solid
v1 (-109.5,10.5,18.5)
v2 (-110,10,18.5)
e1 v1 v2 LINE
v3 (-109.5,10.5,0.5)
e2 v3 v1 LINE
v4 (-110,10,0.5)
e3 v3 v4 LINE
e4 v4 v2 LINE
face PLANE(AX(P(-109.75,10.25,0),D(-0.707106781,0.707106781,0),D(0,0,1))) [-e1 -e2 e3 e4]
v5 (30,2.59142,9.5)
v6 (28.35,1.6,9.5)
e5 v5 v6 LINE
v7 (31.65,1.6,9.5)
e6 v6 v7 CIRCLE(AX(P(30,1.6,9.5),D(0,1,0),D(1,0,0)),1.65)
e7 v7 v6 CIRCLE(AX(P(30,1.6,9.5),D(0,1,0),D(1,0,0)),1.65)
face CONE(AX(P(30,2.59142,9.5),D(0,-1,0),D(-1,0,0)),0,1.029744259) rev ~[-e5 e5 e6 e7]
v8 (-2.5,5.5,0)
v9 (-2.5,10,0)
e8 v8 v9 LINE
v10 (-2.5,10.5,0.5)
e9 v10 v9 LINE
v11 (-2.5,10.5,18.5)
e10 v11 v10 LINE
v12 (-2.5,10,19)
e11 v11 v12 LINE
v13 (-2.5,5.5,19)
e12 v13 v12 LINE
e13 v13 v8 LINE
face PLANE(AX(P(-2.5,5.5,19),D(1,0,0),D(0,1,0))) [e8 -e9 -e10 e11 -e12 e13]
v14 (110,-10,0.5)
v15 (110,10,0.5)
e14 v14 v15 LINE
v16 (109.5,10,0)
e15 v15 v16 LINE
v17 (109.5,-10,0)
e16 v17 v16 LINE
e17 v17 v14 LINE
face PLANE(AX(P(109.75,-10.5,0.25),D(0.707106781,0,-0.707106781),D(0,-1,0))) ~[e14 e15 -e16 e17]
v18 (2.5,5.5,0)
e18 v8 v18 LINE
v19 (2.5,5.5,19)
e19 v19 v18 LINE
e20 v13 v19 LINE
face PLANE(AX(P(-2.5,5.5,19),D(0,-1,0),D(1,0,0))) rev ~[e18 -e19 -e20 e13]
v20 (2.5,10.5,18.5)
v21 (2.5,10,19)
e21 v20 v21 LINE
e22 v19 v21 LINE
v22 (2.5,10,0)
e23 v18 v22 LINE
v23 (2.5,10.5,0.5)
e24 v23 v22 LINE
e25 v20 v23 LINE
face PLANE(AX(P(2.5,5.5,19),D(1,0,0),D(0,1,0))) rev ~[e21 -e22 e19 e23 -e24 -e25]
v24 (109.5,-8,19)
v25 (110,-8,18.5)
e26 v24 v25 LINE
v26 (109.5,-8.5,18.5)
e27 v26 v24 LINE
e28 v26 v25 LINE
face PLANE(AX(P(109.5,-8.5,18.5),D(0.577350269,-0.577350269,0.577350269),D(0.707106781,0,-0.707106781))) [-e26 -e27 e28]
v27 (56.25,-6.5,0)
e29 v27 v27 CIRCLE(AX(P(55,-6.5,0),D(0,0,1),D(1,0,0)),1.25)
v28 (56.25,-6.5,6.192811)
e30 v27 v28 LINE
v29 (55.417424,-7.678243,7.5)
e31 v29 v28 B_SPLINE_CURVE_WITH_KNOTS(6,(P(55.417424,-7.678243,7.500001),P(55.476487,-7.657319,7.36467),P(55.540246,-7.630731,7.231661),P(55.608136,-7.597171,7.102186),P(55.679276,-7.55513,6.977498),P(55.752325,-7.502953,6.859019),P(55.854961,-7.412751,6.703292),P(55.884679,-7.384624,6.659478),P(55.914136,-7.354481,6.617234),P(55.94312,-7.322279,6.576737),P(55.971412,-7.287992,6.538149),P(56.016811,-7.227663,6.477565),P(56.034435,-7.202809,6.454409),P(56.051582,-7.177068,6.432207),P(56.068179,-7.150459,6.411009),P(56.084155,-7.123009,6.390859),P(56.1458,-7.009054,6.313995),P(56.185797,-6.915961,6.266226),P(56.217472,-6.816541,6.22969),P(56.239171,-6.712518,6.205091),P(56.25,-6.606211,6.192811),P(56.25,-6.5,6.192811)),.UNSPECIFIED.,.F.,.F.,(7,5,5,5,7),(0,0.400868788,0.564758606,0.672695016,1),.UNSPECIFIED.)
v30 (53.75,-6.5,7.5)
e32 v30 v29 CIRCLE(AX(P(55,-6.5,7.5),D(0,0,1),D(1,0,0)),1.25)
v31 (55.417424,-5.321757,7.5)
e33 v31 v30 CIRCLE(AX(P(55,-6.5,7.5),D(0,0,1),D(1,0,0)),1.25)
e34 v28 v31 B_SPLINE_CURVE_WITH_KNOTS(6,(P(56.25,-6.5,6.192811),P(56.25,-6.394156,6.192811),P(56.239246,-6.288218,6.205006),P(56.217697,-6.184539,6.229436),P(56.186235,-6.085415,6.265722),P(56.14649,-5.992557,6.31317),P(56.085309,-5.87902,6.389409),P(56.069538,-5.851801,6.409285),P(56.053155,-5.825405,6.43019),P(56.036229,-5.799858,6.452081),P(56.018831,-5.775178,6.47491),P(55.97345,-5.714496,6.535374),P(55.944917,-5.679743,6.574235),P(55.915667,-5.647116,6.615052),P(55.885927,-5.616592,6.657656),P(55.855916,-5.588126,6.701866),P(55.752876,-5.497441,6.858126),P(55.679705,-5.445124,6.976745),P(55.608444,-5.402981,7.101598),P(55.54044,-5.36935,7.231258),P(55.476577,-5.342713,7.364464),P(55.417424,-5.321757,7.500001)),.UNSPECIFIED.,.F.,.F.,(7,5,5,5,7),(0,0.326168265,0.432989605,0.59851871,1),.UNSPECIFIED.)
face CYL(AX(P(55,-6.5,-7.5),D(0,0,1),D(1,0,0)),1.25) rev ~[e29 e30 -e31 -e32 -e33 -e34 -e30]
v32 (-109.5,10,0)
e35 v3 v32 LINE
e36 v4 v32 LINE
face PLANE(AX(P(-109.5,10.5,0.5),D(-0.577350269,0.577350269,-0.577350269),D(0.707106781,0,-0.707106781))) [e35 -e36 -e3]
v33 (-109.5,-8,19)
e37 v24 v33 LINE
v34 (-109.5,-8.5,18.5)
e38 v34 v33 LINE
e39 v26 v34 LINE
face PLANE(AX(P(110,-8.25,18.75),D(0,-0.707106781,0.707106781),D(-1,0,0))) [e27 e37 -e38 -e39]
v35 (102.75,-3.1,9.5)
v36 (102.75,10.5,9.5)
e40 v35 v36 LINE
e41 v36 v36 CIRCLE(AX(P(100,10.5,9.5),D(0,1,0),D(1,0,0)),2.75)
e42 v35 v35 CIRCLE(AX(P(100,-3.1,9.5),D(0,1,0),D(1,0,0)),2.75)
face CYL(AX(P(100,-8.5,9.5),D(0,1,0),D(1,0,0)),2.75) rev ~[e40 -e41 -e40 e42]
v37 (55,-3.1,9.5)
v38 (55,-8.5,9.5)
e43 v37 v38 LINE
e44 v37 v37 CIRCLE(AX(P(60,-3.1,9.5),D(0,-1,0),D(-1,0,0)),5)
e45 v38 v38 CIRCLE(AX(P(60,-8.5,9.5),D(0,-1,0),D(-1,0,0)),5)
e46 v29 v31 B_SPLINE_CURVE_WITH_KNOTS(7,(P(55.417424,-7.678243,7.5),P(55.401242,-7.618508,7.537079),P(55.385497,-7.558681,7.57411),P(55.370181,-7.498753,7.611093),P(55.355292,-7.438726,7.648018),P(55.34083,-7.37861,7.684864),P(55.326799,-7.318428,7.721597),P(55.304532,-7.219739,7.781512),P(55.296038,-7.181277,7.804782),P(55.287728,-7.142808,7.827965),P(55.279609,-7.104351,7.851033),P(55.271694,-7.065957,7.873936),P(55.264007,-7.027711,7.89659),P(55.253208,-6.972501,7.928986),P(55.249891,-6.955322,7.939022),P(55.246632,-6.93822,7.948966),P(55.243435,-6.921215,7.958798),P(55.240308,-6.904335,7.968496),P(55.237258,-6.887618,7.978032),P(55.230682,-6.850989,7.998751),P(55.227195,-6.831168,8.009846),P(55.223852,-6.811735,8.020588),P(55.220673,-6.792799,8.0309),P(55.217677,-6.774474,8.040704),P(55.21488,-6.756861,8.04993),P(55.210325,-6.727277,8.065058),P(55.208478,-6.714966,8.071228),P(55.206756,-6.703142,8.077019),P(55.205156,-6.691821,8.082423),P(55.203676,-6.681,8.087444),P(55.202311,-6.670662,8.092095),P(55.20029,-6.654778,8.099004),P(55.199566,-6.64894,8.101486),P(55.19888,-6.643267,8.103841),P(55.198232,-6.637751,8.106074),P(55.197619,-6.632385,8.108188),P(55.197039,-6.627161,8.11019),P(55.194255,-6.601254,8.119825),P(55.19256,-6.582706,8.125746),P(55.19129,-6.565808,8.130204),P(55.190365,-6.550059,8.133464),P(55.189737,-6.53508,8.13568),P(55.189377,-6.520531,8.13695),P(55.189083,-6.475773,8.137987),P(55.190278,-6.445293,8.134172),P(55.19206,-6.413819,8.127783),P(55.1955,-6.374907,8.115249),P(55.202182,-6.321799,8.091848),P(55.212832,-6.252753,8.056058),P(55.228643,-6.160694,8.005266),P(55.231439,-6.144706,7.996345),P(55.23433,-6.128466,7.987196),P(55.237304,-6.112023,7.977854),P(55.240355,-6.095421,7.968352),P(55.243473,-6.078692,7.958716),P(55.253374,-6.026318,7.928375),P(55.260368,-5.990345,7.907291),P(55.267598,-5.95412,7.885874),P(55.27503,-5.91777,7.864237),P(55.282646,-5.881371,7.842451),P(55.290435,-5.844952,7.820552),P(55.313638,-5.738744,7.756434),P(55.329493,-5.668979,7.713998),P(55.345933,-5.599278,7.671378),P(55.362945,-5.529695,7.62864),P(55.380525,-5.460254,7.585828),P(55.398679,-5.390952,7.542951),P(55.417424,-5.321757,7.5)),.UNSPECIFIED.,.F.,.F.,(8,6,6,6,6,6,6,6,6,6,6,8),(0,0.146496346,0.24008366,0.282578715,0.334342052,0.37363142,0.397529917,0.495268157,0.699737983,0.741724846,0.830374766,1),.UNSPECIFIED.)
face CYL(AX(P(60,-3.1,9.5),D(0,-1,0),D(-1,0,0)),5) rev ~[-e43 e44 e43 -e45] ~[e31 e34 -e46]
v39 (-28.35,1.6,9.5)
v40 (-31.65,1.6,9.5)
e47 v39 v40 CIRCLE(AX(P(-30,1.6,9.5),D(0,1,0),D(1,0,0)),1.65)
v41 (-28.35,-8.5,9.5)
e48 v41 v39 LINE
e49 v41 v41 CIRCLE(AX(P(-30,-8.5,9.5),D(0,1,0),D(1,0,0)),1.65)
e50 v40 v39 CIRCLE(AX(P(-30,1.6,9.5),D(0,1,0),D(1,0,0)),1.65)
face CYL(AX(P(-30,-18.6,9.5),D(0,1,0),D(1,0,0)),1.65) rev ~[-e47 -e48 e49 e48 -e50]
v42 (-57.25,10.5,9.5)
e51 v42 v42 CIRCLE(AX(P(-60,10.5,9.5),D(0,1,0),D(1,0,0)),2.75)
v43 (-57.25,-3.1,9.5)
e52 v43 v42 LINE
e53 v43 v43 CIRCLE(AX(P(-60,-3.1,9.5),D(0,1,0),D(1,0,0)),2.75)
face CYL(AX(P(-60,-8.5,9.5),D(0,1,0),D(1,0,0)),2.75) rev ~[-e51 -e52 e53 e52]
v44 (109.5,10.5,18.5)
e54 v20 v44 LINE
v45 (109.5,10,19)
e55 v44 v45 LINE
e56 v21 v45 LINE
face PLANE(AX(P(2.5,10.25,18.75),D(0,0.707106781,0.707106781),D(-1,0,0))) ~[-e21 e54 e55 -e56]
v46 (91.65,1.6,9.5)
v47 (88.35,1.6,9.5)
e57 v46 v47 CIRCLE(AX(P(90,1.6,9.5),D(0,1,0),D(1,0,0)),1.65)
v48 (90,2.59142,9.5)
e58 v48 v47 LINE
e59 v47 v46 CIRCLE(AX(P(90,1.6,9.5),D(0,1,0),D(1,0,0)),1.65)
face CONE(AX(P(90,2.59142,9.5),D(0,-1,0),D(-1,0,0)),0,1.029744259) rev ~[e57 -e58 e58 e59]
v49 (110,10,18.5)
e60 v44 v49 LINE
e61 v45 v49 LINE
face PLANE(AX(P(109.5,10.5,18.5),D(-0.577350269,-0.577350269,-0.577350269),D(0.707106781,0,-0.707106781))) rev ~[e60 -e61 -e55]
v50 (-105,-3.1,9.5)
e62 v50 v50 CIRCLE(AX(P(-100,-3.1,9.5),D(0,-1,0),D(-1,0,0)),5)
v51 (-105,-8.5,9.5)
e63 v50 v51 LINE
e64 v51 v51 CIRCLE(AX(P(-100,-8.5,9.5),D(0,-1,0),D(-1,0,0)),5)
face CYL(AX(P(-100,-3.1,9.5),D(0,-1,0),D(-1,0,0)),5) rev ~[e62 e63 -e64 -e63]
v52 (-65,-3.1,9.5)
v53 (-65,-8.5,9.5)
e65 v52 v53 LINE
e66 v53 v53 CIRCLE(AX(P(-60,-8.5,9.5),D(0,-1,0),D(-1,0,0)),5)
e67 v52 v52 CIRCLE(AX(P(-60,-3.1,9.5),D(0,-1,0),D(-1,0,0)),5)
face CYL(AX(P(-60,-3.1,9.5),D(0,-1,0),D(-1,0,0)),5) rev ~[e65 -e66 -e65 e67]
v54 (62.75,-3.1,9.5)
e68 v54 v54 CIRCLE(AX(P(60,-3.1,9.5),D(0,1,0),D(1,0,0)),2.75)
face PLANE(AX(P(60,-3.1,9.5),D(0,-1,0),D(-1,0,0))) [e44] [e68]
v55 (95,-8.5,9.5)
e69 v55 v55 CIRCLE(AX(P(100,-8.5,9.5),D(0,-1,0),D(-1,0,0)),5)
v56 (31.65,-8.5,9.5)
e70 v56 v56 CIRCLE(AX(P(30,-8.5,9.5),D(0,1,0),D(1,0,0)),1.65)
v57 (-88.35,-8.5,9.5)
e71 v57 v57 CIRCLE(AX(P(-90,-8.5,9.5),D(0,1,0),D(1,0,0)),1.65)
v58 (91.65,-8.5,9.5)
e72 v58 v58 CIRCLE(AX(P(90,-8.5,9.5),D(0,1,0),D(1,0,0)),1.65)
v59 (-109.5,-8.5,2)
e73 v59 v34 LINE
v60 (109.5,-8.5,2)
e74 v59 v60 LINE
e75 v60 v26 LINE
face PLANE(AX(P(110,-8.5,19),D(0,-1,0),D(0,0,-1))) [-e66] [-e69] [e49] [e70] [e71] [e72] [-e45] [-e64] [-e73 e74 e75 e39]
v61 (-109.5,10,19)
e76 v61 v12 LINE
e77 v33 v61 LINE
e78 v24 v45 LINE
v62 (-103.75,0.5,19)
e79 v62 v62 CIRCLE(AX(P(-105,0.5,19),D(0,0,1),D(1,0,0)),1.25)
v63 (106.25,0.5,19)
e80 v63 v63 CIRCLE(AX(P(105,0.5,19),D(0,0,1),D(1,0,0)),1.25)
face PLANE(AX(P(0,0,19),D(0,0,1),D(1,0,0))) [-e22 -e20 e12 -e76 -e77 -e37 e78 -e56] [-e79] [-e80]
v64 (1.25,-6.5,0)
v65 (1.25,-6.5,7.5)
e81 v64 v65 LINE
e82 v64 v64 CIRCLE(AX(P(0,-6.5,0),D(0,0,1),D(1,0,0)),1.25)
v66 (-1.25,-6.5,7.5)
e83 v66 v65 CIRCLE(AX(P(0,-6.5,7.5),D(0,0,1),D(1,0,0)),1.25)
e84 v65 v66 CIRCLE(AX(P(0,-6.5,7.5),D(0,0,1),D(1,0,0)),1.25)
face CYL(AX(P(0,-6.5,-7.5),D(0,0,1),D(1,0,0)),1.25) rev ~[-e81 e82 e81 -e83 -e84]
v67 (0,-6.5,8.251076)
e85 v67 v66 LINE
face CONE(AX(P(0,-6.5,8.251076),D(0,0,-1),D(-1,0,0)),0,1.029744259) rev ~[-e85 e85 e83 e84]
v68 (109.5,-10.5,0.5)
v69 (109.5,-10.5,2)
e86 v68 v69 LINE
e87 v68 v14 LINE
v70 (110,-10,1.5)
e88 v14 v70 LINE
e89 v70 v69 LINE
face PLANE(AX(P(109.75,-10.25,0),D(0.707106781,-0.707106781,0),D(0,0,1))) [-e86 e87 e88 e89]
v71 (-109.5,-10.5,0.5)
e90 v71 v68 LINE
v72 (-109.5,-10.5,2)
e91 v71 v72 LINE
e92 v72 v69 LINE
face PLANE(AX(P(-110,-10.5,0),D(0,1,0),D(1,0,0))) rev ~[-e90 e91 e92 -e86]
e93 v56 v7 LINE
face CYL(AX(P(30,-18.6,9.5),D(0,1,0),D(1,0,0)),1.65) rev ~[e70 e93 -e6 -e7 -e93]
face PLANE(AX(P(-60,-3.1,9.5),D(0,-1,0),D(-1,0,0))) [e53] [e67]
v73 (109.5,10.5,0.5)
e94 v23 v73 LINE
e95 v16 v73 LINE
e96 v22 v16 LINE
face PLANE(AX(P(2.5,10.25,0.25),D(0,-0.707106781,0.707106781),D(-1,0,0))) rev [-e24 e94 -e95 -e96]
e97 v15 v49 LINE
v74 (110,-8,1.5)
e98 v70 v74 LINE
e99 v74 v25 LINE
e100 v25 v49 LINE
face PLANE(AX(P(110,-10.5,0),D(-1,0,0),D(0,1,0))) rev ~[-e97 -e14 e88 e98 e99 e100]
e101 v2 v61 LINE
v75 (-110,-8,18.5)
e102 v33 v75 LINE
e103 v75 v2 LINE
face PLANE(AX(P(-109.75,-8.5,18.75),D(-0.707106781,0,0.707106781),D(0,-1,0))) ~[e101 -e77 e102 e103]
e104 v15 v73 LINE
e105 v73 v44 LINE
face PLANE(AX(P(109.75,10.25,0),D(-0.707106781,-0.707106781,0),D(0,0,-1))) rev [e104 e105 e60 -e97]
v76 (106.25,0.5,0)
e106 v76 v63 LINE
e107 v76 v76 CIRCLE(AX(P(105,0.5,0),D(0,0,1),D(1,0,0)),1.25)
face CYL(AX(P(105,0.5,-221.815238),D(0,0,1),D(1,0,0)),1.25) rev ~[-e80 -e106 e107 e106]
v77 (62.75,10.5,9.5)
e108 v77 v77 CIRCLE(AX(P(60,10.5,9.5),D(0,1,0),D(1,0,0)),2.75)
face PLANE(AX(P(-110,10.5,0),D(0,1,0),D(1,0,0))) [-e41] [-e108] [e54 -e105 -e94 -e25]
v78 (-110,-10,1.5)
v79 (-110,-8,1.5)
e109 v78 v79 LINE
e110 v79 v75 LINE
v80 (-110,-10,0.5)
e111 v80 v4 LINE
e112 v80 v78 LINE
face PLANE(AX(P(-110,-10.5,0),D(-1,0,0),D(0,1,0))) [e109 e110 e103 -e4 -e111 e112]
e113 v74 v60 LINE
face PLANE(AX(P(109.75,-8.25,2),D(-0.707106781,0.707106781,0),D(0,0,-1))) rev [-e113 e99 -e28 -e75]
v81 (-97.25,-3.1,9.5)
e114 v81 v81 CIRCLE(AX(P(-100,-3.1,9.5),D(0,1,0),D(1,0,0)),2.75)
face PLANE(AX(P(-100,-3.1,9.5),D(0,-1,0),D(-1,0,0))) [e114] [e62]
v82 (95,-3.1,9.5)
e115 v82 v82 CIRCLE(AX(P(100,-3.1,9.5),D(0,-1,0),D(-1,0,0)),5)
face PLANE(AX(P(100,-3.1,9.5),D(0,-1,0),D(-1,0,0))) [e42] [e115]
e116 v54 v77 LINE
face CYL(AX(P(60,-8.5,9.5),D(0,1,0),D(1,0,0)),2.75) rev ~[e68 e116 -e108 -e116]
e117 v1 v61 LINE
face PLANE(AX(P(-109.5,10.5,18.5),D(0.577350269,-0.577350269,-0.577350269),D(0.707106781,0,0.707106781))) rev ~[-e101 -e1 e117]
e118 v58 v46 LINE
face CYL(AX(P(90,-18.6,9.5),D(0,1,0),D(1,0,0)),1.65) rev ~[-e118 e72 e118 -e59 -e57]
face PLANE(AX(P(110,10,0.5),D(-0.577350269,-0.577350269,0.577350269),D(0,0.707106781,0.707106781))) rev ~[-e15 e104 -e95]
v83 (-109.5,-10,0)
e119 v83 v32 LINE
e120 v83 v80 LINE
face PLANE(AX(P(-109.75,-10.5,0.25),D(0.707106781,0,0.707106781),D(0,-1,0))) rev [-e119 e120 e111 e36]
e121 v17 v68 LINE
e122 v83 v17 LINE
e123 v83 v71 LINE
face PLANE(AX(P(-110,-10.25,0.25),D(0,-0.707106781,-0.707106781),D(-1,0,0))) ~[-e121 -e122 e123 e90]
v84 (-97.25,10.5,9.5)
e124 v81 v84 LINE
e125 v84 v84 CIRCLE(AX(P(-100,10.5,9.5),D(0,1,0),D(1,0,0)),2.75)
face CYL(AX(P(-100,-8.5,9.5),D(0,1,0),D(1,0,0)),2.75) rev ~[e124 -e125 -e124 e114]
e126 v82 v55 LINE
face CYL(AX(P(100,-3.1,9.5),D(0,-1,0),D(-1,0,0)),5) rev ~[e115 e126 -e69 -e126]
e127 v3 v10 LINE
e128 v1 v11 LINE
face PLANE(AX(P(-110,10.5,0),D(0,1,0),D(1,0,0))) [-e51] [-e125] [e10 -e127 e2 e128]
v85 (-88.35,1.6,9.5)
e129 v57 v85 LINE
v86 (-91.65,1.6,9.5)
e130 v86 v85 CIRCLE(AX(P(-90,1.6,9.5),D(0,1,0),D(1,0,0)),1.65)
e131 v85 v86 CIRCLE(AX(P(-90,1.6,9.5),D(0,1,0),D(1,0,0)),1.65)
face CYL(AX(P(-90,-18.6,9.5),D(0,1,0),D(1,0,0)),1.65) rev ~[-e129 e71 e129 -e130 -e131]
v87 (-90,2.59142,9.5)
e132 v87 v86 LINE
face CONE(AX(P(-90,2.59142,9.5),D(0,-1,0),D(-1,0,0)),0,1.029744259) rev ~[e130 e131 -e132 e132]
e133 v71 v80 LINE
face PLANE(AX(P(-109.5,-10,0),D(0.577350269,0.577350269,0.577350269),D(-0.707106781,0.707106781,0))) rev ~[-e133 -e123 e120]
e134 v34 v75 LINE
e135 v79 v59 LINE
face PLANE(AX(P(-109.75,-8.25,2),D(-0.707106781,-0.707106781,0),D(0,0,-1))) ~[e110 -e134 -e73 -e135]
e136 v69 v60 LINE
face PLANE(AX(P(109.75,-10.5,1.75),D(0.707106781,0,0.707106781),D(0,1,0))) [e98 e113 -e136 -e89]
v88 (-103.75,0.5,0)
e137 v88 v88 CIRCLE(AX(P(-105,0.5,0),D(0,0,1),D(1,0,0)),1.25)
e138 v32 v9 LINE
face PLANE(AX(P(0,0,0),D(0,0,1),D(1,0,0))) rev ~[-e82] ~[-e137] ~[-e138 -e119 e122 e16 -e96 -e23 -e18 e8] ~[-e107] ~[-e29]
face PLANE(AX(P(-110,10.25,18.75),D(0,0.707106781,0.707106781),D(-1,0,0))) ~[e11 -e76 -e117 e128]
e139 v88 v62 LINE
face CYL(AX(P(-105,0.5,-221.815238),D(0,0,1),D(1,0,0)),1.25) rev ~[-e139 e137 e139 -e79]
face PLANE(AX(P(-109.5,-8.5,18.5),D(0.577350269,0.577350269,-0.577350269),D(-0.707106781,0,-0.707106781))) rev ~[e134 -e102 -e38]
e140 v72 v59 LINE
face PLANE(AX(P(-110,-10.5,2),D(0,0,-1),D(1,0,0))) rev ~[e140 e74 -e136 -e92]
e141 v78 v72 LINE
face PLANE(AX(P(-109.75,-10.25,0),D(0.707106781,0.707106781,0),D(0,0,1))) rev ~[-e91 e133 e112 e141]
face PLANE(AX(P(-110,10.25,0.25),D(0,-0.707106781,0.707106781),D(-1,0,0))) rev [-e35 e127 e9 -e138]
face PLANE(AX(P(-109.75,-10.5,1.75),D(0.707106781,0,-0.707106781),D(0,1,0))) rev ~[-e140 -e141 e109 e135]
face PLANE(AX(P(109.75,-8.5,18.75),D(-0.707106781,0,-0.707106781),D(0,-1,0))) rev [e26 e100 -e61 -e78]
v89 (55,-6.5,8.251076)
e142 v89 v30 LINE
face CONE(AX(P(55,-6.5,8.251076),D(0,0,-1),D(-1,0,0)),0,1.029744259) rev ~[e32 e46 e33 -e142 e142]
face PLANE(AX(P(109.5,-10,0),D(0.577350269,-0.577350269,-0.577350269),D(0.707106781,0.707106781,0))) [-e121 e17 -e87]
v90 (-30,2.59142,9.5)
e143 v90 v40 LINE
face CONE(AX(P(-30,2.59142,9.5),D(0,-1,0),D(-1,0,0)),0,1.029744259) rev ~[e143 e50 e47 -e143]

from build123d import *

# Parameters (mm, degrees)
SKETCH_1_W                   = 220
SKETCH_1_H                   = 21
EXTRUDE_1_DEPTH              = 19
SKETCH_2_W                   = 220
SKETCH_2_H                   = 15
CUT_EXTRUDE_1_DEPTH          = 2
HOLE_WIZARD_M4_1_D           = 3.3
HOLE_WIZARD_M4_1_DEPTH       = 10.1
HOLE_WIZARD_M4_1_TIP         = 0.991420021
HOLE_WIZARD_M5_1_D           = 5.5
HOLE_WIZARD_M5_1_CBORE_D     = 10
HOLE_WIZARD_M5_1_CBORE_DEPTH = 5.4
SKETCH_7_W                   = 5
SKETCH_7_H                   = 5
CUT_EXTRUDE_2_DEPTH          = 113.12158579
HOLE_WIZARD_M3_1_D           = 2.5
HOLE_WIZARD_M3_1_DEPTH       = 7.5
HOLE_WIZARD_M3_1_TIP         = 0.751075774
SKETCH_12_W                  = 2
SKETCH_12_H                  = 2
CUT_EXTRUDE_3_DEPTH          = 222.06842832
CHAMFER_1_SIZE               = 0.5
HOLE_WIZARD_M3_2_D           = 2.5


with BuildPart() as part:
    # 草图1 → 凸台-拉伸1 (new body)
    with BuildSketch(Plane.XY):
        Rectangle(SKETCH_1_W, SKETCH_1_H)
    extrude(amount=EXTRUDE_1_DEPTH)

    # 草图2 → 切除-拉伸1 (cut)
    with BuildSketch(Plane.XZ.offset(10.5)):
        with Locations((0, 9.5)):
            Rectangle(SKETCH_2_W, SKETCH_2_H)
    extrude(amount=-CUT_EXTRUDE_1_DEPTH, mode=Mode.SUBTRACT)

    # M4 螺纹孔1
    with Locations(Plane(origin=(0, -8.5, 0), x_dir=(-1, 0, 0), z_dir=(0, -1, 0))):
        with Locations((-90, -9.5), (-30, -9.5), (30, -9.5), (90, -9.5)):
            Hole(HOLE_WIZARD_M4_1_D / 2, depth=HOLE_WIZARD_M4_1_DEPTH)
            with Locations((0, 0, -(HOLE_WIZARD_M4_1_DEPTH + HOLE_WIZARD_M4_1_TIP / 2))):  # 118° drill point
                Cone(0, HOLE_WIZARD_M4_1_D / 2, HOLE_WIZARD_M4_1_TIP, mode=Mode.SUBTRACT)

    # M5 六角凹头螺钉的柱形沉头孔1 (through all)
    with Locations(Plane(origin=(0, -8.5, 0), x_dir=(-1, 0, 0), z_dir=(0, -1, 0))):
        with Locations((-100, -9.5), (100, -9.5), (60, -9.5), (-60, -9.5)):
            CounterBoreHole(HOLE_WIZARD_M5_1_D / 2, HOLE_WIZARD_M5_1_CBORE_D / 2, HOLE_WIZARD_M5_1_CBORE_DEPTH)

    # 草图7 → 切除-拉伸2 (cut, through all)
    with BuildSketch(Plane.XY.offset(19)):
        with Locations((0, 8)):
            Rectangle(SKETCH_7_W, SKETCH_7_H)
    extrude(amount=-CUT_EXTRUDE_2_DEPTH, mode=Mode.SUBTRACT)

    # M3 螺纹孔1
    with Locations(Plane(origin=(0, 0, 0), x_dir=(-1, 0, 0), z_dir=(0, 0, -1))):
        with Locations((-55, -6.5), (0, -6.5)):
            Hole(HOLE_WIZARD_M3_1_D / 2, depth=HOLE_WIZARD_M3_1_DEPTH)
            with Locations((0, 0, -(HOLE_WIZARD_M3_1_DEPTH + HOLE_WIZARD_M3_1_TIP / 2))):  # 118° drill point
                Cone(0, HOLE_WIZARD_M3_1_D / 2, HOLE_WIZARD_M3_1_TIP, mode=Mode.SUBTRACT)

    # 草图12 → 切除-拉伸3 (cut, through all)
    with BuildSketch(Plane(origin=(110, 0, 0), x_dir=(0, 0, -1), z_dir=(1, 0, 0))):
        with Locations((-18, -9.5)):
            Rectangle(SKETCH_12_W, SKETCH_12_H)
    extrude(amount=-CUT_EXTRUDE_3_DEPTH, mode=Mode.SUBTRACT)

    # 倒角1
    chamfer_1_edges = [part.edges().sort_by_distance(p)[0] for p in [
        (-110, 1, 19),
        (110, 1, 19),
        (0, -8.5, 19),
        (110, -10.5, 1),
        (-110, -10.5, 1),
        (110, -8.5, 10.5),
        (110, -9.5, 2),
        (-110, -8.5, 10.5),
        (-110, -9.5, 2),
        (0, -10.5, 0),
        (-110, 0, 0),
        (56.25, 10.5, 0),
        (110, 0, 0),
        (56.25, 10.5, 19),
        (-110, 10.5, 9.5),
        (110, 10.5, 9.5),
        (-56.25, 10.5, 0),
        (-56.25, 10.5, 19),
    ]]
    chamfer(chamfer_1_edges, length=CHAMFER_1_SIZE)

    # M3 螺纹孔2 (through all)
    with Locations(Plane(origin=(0, 0, 0), x_dir=(-1, 0, 0), z_dir=(0, 0, -1))):
        with Locations((105, 0.5), (-105, 0.5)):
            Hole(HOLE_WIZARD_M3_2_D / 2)


solid = part.part
